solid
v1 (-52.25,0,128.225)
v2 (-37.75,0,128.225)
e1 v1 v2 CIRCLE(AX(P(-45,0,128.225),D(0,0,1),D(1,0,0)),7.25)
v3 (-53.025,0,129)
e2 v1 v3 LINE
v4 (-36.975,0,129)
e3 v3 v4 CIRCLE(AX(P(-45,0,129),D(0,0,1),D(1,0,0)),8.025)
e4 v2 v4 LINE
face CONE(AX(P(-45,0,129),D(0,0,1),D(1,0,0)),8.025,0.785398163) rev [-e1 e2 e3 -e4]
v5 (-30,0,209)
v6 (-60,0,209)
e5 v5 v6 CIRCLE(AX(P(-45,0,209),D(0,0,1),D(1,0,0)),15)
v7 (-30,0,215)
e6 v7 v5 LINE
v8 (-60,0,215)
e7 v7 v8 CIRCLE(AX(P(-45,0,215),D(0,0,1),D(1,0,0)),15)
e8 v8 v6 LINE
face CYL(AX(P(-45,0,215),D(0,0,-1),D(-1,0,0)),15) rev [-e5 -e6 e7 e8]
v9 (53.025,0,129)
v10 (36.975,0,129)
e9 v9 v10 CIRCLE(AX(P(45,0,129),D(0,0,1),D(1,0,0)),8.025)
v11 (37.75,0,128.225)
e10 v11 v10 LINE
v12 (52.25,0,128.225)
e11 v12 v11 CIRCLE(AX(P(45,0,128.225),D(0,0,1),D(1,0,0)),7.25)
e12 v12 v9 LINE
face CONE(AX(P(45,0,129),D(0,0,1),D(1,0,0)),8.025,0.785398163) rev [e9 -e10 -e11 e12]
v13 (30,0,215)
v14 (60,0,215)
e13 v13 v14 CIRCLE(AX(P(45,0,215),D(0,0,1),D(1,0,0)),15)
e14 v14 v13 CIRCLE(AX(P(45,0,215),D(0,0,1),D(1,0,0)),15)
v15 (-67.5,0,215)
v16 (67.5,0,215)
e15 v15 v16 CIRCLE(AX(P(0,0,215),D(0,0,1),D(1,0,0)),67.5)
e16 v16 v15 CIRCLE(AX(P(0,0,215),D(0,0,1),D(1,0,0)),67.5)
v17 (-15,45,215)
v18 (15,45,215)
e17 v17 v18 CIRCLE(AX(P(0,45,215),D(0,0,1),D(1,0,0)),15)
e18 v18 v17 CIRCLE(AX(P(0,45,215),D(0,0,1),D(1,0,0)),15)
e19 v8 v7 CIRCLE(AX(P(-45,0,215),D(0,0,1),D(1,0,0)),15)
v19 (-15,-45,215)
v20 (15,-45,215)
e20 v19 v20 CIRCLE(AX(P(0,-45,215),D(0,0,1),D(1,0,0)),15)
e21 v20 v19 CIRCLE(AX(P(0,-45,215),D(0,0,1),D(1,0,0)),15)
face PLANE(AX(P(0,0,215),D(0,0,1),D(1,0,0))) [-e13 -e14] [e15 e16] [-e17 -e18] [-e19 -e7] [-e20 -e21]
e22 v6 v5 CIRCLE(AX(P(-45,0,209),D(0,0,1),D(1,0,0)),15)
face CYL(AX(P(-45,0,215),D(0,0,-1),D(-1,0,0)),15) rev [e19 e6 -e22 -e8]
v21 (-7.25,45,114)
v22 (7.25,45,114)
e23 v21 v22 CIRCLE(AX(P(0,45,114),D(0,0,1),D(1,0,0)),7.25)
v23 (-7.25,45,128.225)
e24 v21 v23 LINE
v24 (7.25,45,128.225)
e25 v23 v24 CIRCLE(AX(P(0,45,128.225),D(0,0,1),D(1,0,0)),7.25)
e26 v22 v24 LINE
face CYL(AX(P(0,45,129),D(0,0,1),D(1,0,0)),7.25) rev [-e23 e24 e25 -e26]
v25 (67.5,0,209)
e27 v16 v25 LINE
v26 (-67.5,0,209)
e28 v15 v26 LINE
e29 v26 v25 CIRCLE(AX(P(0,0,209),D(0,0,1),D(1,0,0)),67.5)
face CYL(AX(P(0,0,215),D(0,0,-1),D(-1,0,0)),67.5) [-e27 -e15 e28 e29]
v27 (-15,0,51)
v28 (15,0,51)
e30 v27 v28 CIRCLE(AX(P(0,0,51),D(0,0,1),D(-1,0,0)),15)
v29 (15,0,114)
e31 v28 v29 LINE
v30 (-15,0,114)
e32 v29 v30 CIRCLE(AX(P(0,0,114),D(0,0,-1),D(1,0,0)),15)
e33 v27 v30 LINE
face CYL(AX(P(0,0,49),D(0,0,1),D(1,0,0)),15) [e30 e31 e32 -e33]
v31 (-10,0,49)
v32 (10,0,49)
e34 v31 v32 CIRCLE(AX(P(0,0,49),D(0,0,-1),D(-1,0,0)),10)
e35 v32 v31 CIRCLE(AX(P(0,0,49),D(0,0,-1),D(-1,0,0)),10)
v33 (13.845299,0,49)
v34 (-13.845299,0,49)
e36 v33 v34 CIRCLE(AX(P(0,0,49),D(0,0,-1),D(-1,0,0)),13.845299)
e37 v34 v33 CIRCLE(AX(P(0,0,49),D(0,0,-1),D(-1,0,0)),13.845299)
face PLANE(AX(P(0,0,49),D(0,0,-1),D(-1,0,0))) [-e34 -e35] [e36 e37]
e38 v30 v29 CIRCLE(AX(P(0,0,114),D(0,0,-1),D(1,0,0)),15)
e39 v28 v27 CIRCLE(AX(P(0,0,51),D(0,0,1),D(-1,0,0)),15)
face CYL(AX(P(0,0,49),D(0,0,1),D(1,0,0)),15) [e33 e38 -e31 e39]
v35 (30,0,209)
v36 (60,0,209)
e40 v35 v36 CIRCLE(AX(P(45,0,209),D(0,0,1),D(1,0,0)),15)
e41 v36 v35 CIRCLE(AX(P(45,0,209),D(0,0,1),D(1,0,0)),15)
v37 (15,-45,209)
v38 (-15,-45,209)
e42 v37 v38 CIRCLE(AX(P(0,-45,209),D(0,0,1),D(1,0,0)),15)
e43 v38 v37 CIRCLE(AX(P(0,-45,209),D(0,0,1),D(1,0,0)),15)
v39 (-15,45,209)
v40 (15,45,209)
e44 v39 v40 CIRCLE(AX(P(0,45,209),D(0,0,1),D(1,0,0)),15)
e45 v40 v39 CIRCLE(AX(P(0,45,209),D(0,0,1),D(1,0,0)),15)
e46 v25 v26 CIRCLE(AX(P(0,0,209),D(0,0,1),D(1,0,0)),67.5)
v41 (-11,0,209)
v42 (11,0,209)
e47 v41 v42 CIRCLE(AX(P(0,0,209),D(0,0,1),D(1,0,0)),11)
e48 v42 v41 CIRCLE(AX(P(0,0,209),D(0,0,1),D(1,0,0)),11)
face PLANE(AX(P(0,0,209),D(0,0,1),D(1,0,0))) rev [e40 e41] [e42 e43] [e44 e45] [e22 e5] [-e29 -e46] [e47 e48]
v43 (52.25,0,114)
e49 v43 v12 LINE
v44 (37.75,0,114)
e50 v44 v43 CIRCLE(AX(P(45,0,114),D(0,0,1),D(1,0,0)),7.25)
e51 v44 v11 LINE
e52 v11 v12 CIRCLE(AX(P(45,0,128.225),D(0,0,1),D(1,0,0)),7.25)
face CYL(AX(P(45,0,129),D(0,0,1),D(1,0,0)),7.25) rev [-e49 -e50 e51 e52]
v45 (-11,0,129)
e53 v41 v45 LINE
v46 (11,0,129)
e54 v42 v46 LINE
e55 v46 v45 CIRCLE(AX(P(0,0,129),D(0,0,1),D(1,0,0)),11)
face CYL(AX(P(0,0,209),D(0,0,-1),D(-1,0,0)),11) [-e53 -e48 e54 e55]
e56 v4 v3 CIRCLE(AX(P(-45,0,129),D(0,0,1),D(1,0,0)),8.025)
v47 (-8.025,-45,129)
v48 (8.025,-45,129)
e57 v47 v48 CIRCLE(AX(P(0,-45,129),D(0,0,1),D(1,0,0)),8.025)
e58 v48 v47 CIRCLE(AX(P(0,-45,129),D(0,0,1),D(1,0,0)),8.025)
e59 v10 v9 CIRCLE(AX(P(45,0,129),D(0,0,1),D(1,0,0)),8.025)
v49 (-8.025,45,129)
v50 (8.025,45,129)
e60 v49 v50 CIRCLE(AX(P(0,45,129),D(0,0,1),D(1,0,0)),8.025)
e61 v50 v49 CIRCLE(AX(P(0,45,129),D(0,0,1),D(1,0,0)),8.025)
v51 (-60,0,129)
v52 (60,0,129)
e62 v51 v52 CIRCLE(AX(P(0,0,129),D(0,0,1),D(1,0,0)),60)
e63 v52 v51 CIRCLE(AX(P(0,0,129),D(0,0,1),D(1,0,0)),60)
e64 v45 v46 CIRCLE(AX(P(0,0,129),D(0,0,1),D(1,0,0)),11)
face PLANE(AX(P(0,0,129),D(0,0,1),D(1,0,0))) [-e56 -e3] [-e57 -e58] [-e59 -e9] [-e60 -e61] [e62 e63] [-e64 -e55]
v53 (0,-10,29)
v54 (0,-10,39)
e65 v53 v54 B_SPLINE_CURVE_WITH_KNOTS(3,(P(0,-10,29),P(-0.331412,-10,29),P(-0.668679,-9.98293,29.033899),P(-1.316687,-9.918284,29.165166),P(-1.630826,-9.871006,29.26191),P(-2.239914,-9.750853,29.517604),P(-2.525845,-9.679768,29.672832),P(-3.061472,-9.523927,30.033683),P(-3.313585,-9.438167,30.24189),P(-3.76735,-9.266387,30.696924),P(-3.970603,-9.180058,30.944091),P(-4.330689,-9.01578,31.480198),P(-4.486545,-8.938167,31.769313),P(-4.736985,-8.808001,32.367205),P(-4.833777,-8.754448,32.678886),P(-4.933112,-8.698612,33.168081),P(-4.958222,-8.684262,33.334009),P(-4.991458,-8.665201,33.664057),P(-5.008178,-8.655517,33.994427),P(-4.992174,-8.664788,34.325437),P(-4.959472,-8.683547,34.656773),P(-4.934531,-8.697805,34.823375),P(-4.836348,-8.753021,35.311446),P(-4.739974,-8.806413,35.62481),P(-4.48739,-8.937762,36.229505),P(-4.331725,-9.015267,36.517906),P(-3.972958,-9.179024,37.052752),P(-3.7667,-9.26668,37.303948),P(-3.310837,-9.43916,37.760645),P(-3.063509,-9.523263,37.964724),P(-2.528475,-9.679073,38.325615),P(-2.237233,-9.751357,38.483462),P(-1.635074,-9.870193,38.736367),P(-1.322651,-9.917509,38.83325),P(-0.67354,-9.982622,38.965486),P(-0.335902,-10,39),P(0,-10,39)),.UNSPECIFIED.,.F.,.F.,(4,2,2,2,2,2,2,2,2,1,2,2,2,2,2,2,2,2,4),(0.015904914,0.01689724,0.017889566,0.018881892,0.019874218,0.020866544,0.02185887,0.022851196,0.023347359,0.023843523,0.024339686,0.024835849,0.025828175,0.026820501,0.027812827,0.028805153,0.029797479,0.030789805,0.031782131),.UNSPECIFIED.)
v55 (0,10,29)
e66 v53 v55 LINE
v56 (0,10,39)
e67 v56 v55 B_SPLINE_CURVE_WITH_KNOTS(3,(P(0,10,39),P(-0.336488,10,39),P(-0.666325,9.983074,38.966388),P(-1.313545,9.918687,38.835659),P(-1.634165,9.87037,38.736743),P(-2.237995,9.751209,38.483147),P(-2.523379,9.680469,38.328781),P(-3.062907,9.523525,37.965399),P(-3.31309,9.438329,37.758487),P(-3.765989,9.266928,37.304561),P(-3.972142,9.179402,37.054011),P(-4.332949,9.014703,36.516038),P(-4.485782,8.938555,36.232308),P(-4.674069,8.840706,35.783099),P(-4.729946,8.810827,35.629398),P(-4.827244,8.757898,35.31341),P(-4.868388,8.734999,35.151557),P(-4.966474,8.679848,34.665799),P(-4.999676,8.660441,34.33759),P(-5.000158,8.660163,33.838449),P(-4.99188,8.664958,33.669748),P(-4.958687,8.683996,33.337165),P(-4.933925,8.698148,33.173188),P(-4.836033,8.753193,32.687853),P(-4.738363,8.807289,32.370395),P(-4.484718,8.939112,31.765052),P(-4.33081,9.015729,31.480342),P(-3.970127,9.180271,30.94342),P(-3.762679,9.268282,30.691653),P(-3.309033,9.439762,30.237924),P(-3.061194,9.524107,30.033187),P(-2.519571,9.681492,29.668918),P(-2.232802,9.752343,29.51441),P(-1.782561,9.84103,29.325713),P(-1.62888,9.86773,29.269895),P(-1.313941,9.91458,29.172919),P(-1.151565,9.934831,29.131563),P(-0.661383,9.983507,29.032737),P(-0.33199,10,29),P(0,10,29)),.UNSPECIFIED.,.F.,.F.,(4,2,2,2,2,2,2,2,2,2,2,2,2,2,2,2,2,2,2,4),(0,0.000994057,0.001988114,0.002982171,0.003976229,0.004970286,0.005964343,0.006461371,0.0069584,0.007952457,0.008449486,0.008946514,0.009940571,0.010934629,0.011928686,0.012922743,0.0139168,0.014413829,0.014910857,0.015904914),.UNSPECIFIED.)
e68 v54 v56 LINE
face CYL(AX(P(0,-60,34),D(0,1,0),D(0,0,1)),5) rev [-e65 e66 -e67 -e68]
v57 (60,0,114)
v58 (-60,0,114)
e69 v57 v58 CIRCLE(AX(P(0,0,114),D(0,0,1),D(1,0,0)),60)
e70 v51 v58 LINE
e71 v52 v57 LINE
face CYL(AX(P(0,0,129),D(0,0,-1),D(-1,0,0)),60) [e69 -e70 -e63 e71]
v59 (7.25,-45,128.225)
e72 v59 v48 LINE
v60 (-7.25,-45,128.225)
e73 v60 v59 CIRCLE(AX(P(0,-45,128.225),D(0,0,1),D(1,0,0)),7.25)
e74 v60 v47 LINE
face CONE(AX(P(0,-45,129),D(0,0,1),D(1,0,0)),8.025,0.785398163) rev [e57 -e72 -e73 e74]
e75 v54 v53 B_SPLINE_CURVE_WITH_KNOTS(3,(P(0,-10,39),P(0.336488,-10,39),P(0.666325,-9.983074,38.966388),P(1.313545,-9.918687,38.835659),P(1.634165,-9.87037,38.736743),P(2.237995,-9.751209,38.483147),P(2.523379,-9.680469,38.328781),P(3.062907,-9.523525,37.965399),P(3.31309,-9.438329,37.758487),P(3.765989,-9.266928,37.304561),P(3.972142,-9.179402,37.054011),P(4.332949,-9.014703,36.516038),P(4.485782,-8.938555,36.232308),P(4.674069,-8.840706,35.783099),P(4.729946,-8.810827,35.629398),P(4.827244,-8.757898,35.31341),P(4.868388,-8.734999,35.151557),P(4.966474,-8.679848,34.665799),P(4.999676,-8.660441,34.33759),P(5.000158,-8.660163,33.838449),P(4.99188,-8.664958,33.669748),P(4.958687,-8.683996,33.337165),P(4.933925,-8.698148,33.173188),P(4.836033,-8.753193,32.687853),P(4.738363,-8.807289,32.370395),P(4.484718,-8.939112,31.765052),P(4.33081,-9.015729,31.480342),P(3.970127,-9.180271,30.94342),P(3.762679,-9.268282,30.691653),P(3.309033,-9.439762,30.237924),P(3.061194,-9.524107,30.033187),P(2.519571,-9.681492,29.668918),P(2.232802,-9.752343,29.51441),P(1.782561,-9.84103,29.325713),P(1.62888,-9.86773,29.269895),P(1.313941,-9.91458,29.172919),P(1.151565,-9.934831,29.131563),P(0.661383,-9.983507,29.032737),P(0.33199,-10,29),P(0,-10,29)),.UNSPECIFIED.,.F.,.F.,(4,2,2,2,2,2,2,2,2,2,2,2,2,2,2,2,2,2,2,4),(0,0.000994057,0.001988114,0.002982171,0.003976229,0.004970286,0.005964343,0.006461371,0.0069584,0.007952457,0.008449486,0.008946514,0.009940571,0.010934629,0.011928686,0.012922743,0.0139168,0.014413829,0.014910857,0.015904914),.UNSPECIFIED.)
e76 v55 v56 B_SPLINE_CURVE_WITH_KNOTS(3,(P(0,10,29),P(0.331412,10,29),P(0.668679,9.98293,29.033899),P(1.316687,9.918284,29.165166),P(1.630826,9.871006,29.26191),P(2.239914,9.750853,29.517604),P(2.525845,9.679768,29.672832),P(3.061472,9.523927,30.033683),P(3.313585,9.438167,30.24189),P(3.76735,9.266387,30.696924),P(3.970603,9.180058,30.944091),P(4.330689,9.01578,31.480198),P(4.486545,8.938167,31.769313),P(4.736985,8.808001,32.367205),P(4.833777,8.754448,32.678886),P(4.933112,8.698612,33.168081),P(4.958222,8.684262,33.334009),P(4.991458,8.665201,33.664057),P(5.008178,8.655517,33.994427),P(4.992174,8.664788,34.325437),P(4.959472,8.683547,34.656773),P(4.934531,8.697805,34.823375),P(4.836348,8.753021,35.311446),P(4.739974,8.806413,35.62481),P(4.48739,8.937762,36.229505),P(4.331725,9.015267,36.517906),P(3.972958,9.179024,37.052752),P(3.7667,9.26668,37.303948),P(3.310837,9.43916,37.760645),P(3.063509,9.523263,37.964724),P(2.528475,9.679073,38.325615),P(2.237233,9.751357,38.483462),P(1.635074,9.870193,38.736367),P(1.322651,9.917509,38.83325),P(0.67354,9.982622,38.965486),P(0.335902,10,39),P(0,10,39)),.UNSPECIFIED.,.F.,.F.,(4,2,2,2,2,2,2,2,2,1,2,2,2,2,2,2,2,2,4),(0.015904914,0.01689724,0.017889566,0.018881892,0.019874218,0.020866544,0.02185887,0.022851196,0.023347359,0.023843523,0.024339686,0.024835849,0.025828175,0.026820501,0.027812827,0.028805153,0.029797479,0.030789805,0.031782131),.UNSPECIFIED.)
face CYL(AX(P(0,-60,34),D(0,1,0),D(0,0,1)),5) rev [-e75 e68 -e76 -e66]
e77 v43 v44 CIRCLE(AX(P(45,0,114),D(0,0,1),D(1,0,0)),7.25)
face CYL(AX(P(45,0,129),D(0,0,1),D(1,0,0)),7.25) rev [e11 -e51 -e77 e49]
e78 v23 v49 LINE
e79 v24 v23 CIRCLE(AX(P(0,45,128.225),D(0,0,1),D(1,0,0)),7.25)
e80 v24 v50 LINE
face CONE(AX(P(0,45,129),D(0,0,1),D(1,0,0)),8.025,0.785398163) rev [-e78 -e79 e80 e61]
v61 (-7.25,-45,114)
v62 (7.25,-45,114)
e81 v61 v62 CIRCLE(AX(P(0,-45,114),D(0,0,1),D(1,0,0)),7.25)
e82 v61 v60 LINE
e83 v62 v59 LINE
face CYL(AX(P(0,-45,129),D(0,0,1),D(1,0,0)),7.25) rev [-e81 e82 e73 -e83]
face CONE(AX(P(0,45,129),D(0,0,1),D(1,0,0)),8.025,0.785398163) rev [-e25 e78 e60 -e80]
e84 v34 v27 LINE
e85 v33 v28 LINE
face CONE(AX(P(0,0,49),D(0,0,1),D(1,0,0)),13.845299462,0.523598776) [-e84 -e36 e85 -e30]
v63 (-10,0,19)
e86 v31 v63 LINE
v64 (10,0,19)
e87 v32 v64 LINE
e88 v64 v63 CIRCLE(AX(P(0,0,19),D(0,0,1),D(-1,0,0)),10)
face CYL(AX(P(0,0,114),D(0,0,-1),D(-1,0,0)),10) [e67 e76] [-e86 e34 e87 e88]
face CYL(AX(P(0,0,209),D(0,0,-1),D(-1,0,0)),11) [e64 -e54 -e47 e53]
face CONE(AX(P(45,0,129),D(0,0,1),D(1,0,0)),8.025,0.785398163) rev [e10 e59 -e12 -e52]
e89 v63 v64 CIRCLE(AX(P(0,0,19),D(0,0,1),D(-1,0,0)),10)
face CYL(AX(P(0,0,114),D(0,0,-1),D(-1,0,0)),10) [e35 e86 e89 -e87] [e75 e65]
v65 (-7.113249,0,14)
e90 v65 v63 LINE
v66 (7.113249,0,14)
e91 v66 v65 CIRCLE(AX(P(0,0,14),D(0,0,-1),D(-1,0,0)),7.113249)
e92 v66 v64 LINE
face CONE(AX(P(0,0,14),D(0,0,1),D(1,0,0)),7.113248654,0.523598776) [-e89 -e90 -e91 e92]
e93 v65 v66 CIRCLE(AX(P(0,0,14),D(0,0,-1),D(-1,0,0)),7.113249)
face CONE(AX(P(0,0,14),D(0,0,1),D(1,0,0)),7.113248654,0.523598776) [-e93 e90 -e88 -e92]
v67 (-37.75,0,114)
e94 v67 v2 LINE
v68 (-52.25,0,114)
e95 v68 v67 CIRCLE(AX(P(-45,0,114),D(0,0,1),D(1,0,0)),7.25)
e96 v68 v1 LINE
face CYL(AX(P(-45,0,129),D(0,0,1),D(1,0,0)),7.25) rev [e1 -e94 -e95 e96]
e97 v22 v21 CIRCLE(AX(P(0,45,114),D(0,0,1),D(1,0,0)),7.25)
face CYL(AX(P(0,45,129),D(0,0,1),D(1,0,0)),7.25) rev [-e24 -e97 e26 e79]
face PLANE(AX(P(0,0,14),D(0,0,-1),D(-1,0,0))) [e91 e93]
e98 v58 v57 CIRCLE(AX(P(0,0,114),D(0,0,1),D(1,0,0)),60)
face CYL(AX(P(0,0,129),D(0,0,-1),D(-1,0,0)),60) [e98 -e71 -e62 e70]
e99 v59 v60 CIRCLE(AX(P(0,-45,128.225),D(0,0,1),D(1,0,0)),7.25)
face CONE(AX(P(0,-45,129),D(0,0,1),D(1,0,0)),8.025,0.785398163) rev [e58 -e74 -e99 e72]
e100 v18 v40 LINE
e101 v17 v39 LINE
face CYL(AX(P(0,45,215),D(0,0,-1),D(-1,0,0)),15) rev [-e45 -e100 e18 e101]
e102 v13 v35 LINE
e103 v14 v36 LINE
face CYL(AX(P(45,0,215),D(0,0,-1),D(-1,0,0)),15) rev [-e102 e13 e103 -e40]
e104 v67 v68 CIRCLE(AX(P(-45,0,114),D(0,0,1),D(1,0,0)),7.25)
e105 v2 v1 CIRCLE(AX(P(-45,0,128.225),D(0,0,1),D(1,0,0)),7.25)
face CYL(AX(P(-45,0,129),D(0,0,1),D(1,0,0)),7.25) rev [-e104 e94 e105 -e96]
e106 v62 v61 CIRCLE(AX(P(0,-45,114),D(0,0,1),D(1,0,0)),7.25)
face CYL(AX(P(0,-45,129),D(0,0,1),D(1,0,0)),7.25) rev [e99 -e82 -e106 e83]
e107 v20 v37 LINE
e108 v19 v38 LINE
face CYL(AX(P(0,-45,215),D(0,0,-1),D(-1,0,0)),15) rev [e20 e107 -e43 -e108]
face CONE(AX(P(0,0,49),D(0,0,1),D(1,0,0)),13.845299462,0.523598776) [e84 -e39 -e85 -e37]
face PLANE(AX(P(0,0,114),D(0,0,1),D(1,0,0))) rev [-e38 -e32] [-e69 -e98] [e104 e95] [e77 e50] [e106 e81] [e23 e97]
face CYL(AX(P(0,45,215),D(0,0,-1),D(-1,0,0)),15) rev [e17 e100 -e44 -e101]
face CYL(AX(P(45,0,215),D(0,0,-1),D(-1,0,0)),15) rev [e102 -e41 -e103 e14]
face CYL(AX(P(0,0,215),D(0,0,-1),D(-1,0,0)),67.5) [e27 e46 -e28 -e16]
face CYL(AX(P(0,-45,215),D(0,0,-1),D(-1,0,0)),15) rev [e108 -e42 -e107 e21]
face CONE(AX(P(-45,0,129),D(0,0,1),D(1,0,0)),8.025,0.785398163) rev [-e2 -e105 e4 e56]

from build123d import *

# Parameters (mm, degrees)
SKETCH1_R               = 52.5
SKETCH1_R_2             = 3.5
BOSS_EXTRUDE1_DEPTH     = 14
SKETCH2_R               = 10
BOSS_EXTRUDE2_DEPTH     = 100
SKETCH3_R               = 60
BOSS_EXTRUDE3_DEPTH     = 15
CIRPATTERN1_COUNT       = 4
SKETCH6_R               = 67.698937757
CUT_EXTRUDE1_DEPTH      = 14
CHAMFER1_SIZE           = 5
CHAMFER1_SIZE2          = 2.886751346
CUT_EXTRUDE2_DEPTH      = 155.405310789
CUT_EXTRUDE2_DEPTH_BACK = 155.405310789
SKETCH7_R               = 5
SKETCH8_R               = 15
BOSS_EXTRUDE4_DEPTH     = 65
CHAMFER2_SIZE           = 2
CHAMFER2_SIZE2          = 1.154700538
SKETCH9_R               = 11
BOSS_EXTRUDE5_DEPTH     = 80
SKETCH10_R              = 67.5
SKETCH10_R_2            = 15
BOSS_EXTRUDE6_DEPTH     = 6


with BuildPart() as part:
    # Sketch1 → Boss-Extrude1 (new body)
    with BuildSketch(Plane.XY):
        Circle(SKETCH1_R)
        with Locations((0, 45)):
            Circle(SKETCH1_R_2, mode=Mode.SUBTRACT)
        with Locations((38.97114317, 22.5)):
            Circle(SKETCH1_R_2, mode=Mode.SUBTRACT)
        with Locations((38.97114317, -22.5)):
            Circle(SKETCH1_R_2, mode=Mode.SUBTRACT)
        with Locations((0, -45)):
            Circle(SKETCH1_R_2, mode=Mode.SUBTRACT)
        with Locations((-38.97114317, -22.5)):
            Circle(SKETCH1_R_2, mode=Mode.SUBTRACT)
        with Locations((-38.97114317, 22.5)):
            Circle(SKETCH1_R_2, mode=Mode.SUBTRACT)
    extrude(amount=BOSS_EXTRUDE1_DEPTH)

    # Sketch2 → Boss-Extrude2 (add)
    with BuildSketch(Plane.XY.offset(14)):
        Circle(SKETCH2_R)
    extrude(amount=BOSS_EXTRUDE2_DEPTH)

    # Sketch3 → Boss-Extrude3 (add)
    with BuildSketch(Plane.XY.offset(114)):
        Circle(SKETCH3_R)
    extrude(amount=BOSS_EXTRUDE3_DEPTH)

    # Sketch5 → M16x1.5 Tapped Hole1 (revolve, cut)
    with BuildSketch(Plane(origin=(0, 45, 129), x_dir=(0, -1, 0), z_dir=(1, 0, 0))):
        Polygon((0, 0), (0, 40.856239488), (7.25, 36.5), (7.25, 0.775), (8.025, 0), align=None)
    m16x1_5_tapped_hole1 = revolve(axis=Axis((0, 45, 135.35), (0, 0, -1)), mode=Mode.SUBTRACT)

    # CirPattern1: M16x1.5 Tapped Hole1 ×4 about axis
    cirpattern1_axis = Axis((0, 0, 0), (0, 0, 1))
    for i in range(1, CIRPATTERN1_COUNT):
        add(m16x1_5_tapped_hole1.rotate(cirpattern1_axis, i * 360 / CIRPATTERN1_COUNT), mode=Mode.SUBTRACT)

    # Sketch6 → Cut-Extrude1 (cut)
    with BuildSketch(Plane(origin=(0, 0, 0), x_dir=(-1, 0, 0), z_dir=(0, 0, -1))):
        Circle(SKETCH6_R)
    extrude(amount=-CUT_EXTRUDE1_DEPTH, mode=Mode.SUBTRACT)

    # Chamfer1
    chamfer1_edges = [part.edges().sort_by_distance(p)[0] for p in [
        (-10, 0, 14),
    ]]
    chamfer1_side = [part.faces().sort_by_distance(p)[0] for p in [
        (-10, 0, 64),
    ]]
    chamfer(chamfer1_edges, length=CHAMFER1_SIZE, length2=CHAMFER1_SIZE2, reference=chamfer1_side[0])

    # Sketch7 → Cut-Extrude2 (cut, two sides: drawn at the far end of the back side and taken through both)
    with BuildSketch(Plane(origin=(0, 0, 0), x_dir=(1, 0, 0), z_dir=(0, 1, 0)).offset(-CUT_EXTRUDE2_DEPTH_BACK)):
        with Locations(Location((0, -34, 0), (0, 0, 270))):
            Circle(SKETCH7_R)
    extrude(amount=CUT_EXTRUDE2_DEPTH + CUT_EXTRUDE2_DEPTH_BACK, mode=Mode.SUBTRACT)

    # Sketch8 → Boss-Extrude4 (add)
    with BuildSketch(Plane(origin=(0, 0, 114), x_dir=(-1, 0, 0), z_dir=(0, 0, -1))):
        with Locations(Location((0, 0, 0), (0, 0, 180))):
            Circle(SKETCH8_R)
    extrude(amount=BOSS_EXTRUDE4_DEPTH)

    # Chamfer2
    chamfer2_edges = [part.edges().sort_by_distance(p)[0] for p in [
        (-15, 0, 49),
    ]]
    chamfer2_side = [part.faces().sort_by_distance(p)[0] for p in [
        (-15, 0, 81.5),
    ]]
    chamfer(chamfer2_edges, length=CHAMFER2_SIZE, length2=CHAMFER2_SIZE2, reference=chamfer2_side[0])

    # Sketch9 → Boss-Extrude5 (add)
    with BuildSketch(Plane.XY.offset(129)):
        Circle(SKETCH9_R)
    extrude(amount=BOSS_EXTRUDE5_DEPTH)

    # Sketch10 → Boss-Extrude6 (add)
    with BuildSketch(Plane.XY.offset(209)):
        Circle(SKETCH10_R)
        with Locations((0, 45)):
            Circle(SKETCH10_R_2, mode=Mode.SUBTRACT)
        with Locations((45, 0)):
            Circle(SKETCH10_R_2, mode=Mode.SUBTRACT)
        with Locations((0, -45)):
            Circle(SKETCH10_R_2, mode=Mode.SUBTRACT)
        with Locations((-45, 0)):
            Circle(SKETCH10_R_2, mode=Mode.SUBTRACT)
    extrude(amount=BOSS_EXTRUDE6_DEPTH)


solid = part.part
